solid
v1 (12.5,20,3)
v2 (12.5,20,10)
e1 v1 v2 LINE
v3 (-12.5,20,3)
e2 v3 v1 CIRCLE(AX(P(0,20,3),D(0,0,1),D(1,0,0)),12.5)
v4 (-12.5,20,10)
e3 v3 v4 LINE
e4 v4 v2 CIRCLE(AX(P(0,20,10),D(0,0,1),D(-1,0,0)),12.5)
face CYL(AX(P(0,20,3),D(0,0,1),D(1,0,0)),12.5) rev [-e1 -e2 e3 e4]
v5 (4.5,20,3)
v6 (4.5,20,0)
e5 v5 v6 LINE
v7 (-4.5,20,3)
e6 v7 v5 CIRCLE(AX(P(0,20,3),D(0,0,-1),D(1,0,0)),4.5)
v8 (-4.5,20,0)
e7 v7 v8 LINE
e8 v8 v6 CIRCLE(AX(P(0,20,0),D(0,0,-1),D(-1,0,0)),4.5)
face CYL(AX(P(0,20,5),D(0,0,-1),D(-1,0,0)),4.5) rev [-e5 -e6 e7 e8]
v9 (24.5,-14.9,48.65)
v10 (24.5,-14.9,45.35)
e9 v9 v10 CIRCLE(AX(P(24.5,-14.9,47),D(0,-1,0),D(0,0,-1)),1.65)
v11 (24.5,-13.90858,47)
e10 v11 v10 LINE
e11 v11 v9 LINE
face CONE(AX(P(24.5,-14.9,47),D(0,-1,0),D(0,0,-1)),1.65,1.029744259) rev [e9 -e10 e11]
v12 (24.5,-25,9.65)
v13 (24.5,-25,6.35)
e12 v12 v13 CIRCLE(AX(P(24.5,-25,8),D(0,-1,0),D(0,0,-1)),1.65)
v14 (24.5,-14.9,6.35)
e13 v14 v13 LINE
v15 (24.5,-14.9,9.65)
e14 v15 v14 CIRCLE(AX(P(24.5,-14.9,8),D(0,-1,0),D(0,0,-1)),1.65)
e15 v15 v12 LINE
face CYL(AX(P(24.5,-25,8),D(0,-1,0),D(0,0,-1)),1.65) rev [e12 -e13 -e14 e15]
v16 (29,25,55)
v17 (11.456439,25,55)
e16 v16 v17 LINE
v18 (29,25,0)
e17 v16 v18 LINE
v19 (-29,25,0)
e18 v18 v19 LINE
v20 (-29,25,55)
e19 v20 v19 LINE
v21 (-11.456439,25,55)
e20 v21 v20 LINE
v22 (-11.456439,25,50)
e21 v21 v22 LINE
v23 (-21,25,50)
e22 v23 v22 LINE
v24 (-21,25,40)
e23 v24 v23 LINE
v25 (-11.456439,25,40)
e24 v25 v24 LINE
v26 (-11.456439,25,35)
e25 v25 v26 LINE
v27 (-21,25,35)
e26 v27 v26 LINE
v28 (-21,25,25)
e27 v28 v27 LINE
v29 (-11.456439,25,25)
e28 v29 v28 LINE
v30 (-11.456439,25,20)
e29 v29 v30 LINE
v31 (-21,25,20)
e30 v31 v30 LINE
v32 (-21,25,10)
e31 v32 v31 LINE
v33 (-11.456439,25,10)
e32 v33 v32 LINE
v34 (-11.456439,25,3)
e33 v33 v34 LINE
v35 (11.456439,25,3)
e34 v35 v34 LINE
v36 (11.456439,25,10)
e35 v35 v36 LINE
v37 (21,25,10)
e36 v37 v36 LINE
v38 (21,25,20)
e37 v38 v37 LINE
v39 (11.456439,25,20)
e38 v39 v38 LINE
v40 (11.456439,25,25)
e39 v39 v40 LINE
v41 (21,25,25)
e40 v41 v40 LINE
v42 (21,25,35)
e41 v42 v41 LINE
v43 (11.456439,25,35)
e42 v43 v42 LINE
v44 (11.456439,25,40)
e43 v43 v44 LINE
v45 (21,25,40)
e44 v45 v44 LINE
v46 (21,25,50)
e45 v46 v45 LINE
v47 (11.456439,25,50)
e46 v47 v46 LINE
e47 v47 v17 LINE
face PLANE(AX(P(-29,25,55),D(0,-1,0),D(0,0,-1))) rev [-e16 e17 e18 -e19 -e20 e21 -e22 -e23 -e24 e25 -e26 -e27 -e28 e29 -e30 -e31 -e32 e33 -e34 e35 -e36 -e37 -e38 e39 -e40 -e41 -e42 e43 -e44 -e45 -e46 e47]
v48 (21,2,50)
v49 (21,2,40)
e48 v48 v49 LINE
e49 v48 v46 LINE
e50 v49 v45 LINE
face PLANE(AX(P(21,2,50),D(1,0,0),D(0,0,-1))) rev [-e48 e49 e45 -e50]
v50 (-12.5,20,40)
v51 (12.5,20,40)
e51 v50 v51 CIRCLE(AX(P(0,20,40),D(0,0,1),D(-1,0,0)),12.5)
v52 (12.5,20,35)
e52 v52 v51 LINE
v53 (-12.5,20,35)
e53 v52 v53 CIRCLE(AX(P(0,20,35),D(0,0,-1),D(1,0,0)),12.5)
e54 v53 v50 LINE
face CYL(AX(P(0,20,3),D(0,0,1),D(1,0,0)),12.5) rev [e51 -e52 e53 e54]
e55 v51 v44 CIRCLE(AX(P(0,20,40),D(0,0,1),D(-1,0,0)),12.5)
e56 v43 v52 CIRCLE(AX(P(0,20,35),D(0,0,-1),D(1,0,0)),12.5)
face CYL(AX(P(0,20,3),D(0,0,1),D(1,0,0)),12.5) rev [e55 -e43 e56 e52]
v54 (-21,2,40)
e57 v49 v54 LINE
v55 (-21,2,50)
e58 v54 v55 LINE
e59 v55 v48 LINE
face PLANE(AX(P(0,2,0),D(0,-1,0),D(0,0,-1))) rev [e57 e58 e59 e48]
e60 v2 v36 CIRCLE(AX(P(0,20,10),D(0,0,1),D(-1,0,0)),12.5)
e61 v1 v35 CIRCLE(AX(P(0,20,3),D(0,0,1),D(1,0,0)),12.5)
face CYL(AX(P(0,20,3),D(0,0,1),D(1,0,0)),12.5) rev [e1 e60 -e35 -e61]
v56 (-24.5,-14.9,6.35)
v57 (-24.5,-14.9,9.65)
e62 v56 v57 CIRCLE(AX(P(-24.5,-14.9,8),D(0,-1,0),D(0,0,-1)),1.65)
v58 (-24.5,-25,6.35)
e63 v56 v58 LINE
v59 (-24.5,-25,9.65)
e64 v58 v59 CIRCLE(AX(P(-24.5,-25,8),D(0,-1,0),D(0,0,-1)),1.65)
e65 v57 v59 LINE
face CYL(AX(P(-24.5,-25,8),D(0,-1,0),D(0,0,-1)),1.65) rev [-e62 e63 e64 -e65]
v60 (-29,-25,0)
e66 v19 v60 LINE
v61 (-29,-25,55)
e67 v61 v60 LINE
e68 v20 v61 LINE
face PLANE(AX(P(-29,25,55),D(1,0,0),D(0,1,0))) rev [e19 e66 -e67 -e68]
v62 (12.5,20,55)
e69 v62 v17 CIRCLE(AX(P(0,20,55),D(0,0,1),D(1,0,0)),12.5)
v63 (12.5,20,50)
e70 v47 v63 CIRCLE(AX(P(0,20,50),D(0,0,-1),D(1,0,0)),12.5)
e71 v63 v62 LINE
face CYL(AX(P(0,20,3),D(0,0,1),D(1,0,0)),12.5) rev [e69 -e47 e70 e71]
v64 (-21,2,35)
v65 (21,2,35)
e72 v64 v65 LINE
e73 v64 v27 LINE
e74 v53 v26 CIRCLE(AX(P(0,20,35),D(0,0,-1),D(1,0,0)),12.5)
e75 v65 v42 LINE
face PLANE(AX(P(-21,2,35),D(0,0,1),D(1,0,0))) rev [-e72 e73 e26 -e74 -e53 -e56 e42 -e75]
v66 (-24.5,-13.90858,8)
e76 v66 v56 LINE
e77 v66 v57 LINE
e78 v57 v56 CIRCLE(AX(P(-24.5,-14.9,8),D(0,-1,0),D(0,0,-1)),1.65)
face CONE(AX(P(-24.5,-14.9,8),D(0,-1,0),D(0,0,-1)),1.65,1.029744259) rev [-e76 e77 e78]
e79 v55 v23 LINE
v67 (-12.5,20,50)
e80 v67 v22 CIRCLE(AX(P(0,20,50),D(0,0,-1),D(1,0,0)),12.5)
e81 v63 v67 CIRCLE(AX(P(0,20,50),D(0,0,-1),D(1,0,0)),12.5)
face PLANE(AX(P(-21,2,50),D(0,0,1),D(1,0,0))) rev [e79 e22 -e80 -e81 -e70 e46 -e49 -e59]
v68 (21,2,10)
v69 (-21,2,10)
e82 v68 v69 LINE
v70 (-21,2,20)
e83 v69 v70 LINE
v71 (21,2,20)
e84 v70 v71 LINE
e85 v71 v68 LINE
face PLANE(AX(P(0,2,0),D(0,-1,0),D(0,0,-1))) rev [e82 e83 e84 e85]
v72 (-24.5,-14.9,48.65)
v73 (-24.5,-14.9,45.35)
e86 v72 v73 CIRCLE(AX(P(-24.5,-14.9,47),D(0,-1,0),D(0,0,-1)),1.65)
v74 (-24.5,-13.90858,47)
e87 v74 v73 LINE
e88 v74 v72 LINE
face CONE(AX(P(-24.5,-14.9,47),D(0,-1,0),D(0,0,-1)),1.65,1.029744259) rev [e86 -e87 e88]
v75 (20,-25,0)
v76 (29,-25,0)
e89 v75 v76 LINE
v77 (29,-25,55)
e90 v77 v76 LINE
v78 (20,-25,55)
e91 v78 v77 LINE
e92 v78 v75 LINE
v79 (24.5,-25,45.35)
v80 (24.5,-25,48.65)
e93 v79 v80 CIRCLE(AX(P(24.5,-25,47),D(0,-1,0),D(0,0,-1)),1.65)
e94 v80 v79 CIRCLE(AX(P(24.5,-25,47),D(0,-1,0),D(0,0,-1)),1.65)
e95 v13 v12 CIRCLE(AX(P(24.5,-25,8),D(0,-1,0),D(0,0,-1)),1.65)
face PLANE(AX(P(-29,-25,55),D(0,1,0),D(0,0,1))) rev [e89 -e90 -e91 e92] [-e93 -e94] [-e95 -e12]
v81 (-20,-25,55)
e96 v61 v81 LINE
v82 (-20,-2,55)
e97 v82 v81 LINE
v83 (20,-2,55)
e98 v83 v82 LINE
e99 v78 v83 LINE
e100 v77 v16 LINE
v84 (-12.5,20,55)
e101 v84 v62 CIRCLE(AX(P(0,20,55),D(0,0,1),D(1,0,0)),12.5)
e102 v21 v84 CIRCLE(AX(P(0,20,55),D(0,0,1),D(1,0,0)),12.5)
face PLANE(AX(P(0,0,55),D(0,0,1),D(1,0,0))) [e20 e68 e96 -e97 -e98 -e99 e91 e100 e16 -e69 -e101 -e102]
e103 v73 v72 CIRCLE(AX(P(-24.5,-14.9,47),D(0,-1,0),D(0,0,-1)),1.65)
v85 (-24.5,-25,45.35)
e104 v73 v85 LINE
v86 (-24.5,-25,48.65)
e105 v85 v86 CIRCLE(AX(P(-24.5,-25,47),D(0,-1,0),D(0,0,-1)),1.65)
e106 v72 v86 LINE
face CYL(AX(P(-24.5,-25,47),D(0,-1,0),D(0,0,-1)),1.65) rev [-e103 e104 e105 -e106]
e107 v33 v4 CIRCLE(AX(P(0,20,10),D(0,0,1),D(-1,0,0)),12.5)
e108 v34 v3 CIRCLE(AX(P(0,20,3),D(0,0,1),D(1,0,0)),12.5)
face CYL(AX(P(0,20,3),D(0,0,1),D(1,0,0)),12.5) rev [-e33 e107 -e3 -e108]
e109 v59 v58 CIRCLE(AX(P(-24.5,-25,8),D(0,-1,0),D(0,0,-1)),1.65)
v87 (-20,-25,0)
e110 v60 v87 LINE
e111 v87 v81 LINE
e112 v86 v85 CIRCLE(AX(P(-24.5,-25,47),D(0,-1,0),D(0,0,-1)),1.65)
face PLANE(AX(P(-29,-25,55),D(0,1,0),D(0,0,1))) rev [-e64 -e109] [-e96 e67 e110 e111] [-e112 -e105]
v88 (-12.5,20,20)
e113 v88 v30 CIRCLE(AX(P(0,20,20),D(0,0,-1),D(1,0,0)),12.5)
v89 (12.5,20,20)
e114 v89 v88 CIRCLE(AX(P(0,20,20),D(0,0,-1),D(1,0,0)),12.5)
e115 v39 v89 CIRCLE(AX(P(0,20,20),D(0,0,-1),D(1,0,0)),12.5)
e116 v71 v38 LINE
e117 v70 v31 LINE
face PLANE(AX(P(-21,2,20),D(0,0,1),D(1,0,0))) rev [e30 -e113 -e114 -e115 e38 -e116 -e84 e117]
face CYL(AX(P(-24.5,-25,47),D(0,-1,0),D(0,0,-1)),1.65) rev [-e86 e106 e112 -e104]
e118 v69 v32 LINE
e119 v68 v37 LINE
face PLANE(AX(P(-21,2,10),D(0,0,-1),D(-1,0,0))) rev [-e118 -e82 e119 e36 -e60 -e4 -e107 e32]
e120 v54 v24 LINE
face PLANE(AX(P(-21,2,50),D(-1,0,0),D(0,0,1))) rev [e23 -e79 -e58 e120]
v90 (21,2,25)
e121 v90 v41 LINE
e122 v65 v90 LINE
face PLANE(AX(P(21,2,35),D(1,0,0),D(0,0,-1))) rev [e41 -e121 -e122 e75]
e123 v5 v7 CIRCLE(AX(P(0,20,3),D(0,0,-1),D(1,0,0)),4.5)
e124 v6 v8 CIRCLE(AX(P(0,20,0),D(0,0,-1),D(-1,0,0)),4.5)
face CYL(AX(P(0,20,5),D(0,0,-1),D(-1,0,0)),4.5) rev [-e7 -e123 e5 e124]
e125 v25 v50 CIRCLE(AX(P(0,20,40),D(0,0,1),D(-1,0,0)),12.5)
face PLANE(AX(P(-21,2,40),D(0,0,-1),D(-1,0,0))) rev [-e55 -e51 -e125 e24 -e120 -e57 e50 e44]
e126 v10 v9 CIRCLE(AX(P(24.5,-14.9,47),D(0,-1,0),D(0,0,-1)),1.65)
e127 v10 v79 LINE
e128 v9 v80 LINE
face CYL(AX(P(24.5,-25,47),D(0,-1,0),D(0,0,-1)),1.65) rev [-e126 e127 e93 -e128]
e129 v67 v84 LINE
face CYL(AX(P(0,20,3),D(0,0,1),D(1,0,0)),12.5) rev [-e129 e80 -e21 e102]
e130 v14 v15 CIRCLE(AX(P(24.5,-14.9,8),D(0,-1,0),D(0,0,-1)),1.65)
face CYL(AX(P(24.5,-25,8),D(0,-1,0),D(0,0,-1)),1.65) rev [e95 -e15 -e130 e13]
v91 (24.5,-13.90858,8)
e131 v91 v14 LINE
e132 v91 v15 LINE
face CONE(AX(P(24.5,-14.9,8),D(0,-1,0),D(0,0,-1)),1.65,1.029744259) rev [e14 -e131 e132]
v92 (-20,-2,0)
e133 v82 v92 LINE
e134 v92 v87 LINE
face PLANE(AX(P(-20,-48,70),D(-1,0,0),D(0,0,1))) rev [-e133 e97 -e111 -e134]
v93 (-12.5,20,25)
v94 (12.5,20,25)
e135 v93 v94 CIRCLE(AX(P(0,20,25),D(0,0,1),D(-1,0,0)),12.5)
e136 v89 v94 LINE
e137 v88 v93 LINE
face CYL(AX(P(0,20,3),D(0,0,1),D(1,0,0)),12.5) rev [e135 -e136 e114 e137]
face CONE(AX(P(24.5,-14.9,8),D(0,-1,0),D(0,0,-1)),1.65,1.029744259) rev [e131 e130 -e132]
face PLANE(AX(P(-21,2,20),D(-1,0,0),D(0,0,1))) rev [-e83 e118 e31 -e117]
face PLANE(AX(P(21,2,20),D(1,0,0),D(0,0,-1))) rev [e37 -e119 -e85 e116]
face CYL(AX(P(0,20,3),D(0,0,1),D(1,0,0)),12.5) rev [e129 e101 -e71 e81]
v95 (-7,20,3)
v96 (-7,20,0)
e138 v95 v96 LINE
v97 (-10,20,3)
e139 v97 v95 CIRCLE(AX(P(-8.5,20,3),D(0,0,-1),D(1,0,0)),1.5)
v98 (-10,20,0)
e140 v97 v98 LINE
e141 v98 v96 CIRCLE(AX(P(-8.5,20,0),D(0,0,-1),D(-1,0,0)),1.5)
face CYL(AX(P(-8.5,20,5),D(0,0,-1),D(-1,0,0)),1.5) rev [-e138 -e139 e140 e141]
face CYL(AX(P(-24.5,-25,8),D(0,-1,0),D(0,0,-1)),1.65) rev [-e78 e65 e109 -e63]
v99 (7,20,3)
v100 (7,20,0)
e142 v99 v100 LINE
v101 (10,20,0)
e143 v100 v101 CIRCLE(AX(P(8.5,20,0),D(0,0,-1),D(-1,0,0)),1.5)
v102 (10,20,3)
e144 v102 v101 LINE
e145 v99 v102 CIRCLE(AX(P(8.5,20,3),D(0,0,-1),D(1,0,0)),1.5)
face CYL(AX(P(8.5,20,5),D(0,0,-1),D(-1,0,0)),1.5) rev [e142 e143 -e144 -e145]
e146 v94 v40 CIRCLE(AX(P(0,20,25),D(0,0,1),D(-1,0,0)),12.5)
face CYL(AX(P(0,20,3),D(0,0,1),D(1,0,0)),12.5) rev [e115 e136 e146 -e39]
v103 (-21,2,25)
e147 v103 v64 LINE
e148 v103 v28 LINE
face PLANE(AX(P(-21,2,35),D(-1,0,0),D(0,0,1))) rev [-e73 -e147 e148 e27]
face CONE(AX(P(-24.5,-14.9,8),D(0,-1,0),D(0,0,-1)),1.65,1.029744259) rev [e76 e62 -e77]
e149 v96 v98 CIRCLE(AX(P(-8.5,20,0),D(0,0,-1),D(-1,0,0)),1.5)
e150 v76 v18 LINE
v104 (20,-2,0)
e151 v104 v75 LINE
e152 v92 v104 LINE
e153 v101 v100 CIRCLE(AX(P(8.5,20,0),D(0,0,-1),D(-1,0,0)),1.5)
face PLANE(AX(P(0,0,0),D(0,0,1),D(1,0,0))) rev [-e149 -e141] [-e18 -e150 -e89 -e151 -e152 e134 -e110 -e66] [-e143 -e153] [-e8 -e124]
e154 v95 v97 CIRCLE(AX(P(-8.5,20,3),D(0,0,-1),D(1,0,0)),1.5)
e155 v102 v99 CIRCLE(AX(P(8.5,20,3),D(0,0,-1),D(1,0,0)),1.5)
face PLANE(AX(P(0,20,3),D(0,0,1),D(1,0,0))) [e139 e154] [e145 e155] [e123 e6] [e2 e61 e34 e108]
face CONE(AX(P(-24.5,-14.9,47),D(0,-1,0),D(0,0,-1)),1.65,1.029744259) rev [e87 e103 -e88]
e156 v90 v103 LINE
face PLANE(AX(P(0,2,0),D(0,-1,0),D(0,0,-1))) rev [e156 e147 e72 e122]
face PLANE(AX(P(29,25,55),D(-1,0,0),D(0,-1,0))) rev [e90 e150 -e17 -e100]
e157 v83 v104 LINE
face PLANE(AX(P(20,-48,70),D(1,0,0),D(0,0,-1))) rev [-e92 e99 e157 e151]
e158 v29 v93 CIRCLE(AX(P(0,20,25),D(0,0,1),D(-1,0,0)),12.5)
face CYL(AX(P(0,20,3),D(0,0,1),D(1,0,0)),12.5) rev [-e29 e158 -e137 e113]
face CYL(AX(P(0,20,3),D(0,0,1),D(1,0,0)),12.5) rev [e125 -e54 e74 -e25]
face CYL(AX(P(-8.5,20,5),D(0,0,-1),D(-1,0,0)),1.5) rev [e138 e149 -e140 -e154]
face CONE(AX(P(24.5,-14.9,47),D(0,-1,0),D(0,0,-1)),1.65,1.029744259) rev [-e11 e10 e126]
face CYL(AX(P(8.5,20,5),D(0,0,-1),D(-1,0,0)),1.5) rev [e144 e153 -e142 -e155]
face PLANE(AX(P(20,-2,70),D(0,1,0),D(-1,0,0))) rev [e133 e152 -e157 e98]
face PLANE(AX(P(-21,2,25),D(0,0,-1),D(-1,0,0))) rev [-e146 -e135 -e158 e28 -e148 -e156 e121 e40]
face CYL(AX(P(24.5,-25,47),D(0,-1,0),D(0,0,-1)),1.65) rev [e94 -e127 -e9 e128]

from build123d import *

# Parameters (mm, degrees)
SKETCH1_W             = 58
SKETCH1_H             = 50
BOSS_EXTRUDE1_DEPTH   = 55
SKETCH3_R             = 4.5
SKETCH3_R_2           = 1.5
CUT_EXTRUDE2_DEPTH    = 5
SKETCH2_R             = 12.5
CUT_EXTRUDE1_DEPTH    = 52
SKETCH4_W             = 40
SKETCH4_H             = 46
CUT_EXTRUDE3_DEPTH    = 70
M4_TAPPED_HOLE1_D     = 3.3
M4_TAPPED_HOLE1_DEPTH = 10.1
M4_TAPPED_HOLE1_TIP   = 0.991420021
SKETCH8_W             = 42
SKETCH8_H             = 10
CUT_EXTRUDE4_DEPTH    = 23


with BuildPart() as part:
    # Sketch1 → Boss-Extrude1 (new body)
    with BuildSketch(Plane.XY):
        Rectangle(SKETCH1_W, SKETCH1_H)
    extrude(amount=BOSS_EXTRUDE1_DEPTH)

    # Sketch3 → Cut-Extrude2 (cut)
    with BuildSketch(Plane(origin=(0, 0, 0), x_dir=(-1, 0, 0), z_dir=(0, 0, -1))):
        with Locations((0, 20)):
            Circle(SKETCH3_R)
        with Locations((-8.5, 20)):
            Circle(SKETCH3_R_2)
        with Locations((8.5, 20)):
            Circle(SKETCH3_R_2)
    extrude(amount=-CUT_EXTRUDE2_DEPTH, mode=Mode.SUBTRACT)

    # Sketch2 → Cut-Extrude1 (cut)
    with BuildSketch(Plane.XY.offset(55)):
        with Locations((0, 20)):
            Circle(SKETCH2_R)
    extrude(amount=-CUT_EXTRUDE1_DEPTH, mode=Mode.SUBTRACT)

    # Sketch4 → Cut-Extrude3 (cut)
    with BuildSketch(Plane(origin=(0, 0, 0), x_dir=(-1, 0, 0), z_dir=(0, 0, -1))):
        with Locations((0, -25)):
            Rectangle(SKETCH4_W, SKETCH4_H)
    extrude(amount=-CUT_EXTRUDE3_DEPTH, mode=Mode.SUBTRACT)

    # M4 Tapped Hole1
    with Locations(Plane(origin=(0, -25, 0), x_dir=(-1, 0, 0), z_dir=(0, -1, 0))):
        with Locations((24.5, -47), (24.5, -8), (-24.5, -8), (-24.5, -47)):
            Hole(M4_TAPPED_HOLE1_D / 2, depth=M4_TAPPED_HOLE1_DEPTH)
            with Locations((0, 0, -(M4_TAPPED_HOLE1_DEPTH + M4_TAPPED_HOLE1_TIP / 2))):  # 118° drill point
                Cone(0, M4_TAPPED_HOLE1_D / 2, M4_TAPPED_HOLE1_TIP, mode=Mode.SUBTRACT)

    # Sketch8 → Cut-Extrude4 (cut)
    with BuildSketch(Plane(origin=(0, 25, 0), x_dir=(1, 0, 0), z_dir=(0, 1, 0))):
        with Locations((0, -15)):
            Rectangle(SKETCH8_W, SKETCH8_H)
        with Locations((0, -30)):
            Rectangle(SKETCH8_W, SKETCH8_H)
        with Locations((0, -45)):
            Rectangle(SKETCH8_W, SKETCH8_H)
    extrude(amount=-CUT_EXTRUDE4_DEPTH, mode=Mode.SUBTRACT)


solid = part.part
